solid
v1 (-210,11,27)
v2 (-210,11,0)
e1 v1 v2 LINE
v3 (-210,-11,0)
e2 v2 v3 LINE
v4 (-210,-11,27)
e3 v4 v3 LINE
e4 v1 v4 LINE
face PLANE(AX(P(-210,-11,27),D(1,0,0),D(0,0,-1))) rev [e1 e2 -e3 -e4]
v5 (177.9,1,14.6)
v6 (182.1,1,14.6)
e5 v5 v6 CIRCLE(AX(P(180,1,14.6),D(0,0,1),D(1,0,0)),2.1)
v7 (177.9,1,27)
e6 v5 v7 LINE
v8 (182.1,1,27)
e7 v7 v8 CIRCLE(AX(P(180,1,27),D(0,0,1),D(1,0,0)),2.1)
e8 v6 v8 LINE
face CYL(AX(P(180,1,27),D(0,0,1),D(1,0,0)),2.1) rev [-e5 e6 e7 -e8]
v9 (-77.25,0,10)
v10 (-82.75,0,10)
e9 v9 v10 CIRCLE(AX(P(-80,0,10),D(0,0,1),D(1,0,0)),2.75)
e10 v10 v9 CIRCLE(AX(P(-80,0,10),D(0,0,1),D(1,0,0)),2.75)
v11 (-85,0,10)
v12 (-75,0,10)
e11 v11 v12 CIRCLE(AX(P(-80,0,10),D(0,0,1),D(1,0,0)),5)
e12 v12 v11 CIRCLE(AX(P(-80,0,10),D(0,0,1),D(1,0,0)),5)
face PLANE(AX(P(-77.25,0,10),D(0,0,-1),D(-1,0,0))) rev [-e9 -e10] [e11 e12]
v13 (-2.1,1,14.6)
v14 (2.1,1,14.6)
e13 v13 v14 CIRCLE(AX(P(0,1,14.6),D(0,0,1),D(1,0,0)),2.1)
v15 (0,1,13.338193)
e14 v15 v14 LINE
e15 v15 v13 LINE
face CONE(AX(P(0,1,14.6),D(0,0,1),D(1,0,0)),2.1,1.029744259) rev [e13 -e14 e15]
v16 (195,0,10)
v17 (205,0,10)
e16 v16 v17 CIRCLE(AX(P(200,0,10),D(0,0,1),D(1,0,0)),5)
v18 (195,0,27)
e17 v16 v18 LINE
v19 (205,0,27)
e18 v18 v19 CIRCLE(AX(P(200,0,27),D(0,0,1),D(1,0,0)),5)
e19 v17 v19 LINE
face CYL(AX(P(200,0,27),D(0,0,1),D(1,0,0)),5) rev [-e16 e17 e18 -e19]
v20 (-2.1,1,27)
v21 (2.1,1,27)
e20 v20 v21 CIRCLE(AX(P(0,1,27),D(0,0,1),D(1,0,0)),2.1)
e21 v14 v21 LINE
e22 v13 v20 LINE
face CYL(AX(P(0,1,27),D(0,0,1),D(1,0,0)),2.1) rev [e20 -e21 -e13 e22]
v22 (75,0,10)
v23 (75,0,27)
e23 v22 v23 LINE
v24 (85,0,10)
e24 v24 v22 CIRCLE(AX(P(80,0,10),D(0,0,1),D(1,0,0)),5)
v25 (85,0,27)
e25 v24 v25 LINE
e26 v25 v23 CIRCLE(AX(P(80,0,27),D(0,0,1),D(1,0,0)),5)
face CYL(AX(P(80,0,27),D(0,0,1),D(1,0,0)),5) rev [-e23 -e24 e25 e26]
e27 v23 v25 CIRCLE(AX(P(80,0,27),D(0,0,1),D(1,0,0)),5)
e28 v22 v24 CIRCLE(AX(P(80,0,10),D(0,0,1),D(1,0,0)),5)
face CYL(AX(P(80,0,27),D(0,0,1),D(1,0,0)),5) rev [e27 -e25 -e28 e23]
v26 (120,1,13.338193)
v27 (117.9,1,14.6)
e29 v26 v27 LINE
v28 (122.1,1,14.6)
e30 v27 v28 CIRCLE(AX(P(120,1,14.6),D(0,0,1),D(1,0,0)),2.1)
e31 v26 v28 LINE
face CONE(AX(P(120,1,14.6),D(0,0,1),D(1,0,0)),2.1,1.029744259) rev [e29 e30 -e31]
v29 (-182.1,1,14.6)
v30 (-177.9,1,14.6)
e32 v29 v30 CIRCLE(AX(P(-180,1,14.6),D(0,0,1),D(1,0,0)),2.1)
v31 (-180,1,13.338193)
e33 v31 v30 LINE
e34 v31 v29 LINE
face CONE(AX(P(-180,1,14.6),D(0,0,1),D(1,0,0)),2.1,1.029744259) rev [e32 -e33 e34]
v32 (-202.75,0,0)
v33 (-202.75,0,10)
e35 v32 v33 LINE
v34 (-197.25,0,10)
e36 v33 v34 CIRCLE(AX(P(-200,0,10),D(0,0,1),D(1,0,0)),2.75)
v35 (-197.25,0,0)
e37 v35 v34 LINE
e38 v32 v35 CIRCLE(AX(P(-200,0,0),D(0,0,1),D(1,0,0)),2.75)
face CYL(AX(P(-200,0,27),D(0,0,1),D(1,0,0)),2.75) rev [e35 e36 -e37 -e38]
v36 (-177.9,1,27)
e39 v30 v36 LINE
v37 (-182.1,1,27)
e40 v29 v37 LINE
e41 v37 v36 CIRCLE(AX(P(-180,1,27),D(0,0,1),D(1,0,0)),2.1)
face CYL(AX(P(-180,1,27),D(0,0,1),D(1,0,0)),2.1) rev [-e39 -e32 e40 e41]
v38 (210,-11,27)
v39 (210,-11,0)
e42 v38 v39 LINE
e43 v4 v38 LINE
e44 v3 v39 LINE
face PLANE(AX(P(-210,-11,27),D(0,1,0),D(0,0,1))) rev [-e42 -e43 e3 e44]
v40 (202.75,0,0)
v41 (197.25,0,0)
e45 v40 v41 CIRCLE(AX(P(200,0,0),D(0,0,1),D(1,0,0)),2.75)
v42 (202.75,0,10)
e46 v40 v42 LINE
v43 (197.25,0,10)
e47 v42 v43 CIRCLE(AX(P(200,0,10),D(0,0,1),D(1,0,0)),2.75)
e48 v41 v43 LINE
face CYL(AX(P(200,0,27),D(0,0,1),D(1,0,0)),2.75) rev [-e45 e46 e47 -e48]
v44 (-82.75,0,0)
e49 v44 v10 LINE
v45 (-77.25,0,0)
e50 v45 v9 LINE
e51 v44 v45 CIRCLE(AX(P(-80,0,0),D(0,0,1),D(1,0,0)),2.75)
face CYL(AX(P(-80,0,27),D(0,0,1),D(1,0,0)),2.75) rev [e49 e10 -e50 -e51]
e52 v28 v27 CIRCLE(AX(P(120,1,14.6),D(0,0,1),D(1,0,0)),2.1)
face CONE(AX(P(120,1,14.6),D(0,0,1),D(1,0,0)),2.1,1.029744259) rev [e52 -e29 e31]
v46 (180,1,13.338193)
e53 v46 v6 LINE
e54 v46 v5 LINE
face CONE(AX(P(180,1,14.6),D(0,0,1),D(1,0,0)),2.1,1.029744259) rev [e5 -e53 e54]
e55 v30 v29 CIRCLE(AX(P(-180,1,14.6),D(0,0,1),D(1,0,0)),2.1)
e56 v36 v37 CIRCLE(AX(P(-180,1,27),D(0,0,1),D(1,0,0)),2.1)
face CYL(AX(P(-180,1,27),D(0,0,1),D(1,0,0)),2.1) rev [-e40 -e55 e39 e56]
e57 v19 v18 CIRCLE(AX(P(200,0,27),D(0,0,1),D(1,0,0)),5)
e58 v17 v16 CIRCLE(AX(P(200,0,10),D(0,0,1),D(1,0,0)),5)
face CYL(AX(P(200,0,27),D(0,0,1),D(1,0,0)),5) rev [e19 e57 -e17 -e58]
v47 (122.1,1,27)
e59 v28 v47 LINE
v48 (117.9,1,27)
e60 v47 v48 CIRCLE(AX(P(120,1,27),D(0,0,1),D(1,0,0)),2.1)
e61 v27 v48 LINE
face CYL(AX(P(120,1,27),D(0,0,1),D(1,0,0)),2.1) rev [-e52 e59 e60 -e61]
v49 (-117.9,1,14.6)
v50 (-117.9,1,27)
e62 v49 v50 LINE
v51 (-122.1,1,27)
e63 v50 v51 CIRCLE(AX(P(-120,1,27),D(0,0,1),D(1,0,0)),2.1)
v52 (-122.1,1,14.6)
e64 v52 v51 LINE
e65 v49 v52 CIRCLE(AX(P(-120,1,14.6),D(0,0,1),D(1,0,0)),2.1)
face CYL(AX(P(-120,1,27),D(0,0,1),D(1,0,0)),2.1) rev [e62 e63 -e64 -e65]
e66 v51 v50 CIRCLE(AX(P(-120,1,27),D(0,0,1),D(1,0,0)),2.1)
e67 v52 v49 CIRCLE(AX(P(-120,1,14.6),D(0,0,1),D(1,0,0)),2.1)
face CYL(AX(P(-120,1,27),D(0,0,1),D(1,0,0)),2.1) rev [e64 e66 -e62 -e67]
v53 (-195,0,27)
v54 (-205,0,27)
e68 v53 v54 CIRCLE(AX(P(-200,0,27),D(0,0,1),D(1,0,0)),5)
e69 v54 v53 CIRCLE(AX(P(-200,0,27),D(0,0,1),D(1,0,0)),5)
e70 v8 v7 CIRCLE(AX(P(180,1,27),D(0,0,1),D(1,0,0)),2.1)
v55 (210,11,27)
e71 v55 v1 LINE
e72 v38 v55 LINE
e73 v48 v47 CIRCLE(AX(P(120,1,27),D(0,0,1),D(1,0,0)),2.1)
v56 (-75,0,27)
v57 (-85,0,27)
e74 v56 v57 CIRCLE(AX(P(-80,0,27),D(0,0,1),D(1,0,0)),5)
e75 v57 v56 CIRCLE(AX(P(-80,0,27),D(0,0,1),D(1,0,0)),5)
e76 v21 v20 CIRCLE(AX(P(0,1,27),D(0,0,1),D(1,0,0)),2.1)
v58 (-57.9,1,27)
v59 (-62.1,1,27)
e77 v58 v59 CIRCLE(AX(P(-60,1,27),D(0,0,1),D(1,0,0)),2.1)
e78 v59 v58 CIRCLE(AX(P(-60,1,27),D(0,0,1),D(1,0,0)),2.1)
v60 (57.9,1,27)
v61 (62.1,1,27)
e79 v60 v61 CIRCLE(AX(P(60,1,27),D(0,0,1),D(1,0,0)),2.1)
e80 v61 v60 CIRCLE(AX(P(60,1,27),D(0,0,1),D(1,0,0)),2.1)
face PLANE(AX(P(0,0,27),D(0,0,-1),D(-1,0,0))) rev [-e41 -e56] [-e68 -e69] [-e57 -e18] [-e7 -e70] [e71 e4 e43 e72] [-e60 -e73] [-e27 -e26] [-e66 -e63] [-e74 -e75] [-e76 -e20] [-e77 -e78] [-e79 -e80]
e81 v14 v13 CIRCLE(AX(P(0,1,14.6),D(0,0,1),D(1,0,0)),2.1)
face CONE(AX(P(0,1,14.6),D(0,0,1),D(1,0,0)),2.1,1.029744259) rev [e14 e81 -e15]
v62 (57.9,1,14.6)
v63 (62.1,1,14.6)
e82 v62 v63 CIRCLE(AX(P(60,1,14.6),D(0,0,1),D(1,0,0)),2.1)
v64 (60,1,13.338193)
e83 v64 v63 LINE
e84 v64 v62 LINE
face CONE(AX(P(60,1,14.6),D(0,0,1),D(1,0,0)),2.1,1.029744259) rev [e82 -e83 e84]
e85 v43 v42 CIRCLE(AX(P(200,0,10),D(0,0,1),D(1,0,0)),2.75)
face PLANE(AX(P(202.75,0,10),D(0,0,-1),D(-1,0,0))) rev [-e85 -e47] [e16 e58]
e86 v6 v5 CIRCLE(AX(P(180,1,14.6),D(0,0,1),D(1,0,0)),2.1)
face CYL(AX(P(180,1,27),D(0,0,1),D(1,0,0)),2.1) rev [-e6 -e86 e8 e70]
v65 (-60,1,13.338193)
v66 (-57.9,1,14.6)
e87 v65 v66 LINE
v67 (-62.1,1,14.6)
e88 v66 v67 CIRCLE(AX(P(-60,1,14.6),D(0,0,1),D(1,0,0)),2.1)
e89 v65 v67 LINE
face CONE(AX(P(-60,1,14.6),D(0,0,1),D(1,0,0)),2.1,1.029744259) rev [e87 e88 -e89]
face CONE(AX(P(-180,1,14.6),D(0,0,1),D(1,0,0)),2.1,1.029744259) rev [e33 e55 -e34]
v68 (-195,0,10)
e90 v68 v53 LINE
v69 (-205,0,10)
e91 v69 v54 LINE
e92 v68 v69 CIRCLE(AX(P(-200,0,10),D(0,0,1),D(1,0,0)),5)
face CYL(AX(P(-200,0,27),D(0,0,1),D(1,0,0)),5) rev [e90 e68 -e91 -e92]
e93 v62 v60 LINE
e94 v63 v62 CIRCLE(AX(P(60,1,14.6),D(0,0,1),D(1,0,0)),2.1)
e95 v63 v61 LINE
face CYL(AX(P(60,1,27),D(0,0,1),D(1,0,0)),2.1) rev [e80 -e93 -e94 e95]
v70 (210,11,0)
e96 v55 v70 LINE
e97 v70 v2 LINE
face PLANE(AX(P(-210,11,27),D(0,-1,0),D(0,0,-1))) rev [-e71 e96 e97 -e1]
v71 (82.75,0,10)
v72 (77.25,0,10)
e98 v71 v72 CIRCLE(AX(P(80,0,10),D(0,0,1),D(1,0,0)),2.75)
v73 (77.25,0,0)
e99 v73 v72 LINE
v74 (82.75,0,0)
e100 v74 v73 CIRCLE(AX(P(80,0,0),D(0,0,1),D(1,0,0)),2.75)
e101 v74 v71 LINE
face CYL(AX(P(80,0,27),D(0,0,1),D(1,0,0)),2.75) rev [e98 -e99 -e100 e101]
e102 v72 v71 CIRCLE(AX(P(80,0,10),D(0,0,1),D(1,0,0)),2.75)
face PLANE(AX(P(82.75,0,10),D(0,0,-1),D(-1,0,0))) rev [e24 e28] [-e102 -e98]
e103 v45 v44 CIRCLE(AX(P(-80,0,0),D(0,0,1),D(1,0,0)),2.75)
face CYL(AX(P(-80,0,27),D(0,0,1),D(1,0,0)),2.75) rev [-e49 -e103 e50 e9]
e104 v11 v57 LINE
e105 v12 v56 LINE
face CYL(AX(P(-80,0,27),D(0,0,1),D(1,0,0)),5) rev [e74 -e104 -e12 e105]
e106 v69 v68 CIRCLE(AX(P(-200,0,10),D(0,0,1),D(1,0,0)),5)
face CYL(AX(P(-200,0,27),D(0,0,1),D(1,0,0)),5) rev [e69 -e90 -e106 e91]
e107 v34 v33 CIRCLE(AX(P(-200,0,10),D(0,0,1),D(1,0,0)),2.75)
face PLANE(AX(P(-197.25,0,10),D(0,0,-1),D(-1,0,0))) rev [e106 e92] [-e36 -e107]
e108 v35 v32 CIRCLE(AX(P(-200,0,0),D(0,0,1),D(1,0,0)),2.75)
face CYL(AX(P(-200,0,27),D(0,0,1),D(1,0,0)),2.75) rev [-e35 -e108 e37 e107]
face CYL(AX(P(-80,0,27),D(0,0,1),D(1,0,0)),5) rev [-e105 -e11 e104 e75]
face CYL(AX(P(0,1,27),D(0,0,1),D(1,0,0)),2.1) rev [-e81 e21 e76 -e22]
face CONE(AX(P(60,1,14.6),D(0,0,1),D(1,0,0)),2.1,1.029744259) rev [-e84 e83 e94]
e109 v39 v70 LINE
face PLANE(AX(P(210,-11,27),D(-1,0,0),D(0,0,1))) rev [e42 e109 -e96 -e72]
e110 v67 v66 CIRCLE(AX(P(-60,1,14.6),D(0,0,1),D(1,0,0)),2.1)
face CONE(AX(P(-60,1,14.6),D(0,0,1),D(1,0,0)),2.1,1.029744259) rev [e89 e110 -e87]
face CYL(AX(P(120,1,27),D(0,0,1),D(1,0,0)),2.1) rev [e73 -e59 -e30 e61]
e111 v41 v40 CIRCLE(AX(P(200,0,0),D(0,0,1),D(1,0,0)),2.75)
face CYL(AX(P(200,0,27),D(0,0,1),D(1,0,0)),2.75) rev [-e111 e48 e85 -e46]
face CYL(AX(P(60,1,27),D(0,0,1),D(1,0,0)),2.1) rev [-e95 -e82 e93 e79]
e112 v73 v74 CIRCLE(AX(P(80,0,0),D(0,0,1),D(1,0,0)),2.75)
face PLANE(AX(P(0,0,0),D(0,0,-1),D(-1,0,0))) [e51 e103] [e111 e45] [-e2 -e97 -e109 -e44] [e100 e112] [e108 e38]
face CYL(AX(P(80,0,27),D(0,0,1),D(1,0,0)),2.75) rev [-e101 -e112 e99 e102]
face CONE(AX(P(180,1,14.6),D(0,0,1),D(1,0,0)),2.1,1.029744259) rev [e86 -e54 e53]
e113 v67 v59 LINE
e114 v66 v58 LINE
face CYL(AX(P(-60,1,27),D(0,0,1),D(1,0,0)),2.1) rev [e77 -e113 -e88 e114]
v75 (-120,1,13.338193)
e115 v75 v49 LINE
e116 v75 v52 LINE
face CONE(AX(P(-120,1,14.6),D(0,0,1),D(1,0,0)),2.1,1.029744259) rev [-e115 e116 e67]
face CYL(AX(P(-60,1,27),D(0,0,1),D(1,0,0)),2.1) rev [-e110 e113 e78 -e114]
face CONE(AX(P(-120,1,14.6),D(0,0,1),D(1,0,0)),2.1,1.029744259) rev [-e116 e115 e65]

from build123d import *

# Parameters (mm, degrees)
SKETCH1_W                                           = 420
SKETCH1_H                                           = 22
BOSS_EXTRUDE1_DEPTH                                 = 27
M5_TAPPED_HOLE1_D                                   = 4.2
M5_TAPPED_HOLE1_DEPTH                               = 12.4
M5_TAPPED_HOLE1_TIP                                 = 1.2618073
CBORE_FOR_M5_HEX_SOCKET_HEAD_CAP_SCREW1_D           = 5.5
CBORE_FOR_M5_HEX_SOCKET_HEAD_CAP_SCREW1_CBORE_D     = 10
CBORE_FOR_M5_HEX_SOCKET_HEAD_CAP_SCREW1_CBORE_DEPTH = 17


with BuildPart() as part:
    # Sketch1 → Boss-Extrude1 (new body)
    with BuildSketch(Plane.XY):
        Rectangle(SKETCH1_W, SKETCH1_H)
    extrude(amount=BOSS_EXTRUDE1_DEPTH)

    # M5 Tapped Hole1
    with Locations(Plane.XY.offset(27)):
        with Locations((-180, 1), (-120, 1), (-60, 1), (0, 1), (60, 1), (120, 1), (180, 1)):
            Hole(M5_TAPPED_HOLE1_D / 2, depth=M5_TAPPED_HOLE1_DEPTH)
            with Locations((0, 0, -(M5_TAPPED_HOLE1_DEPTH + M5_TAPPED_HOLE1_TIP / 2))):  # 118° drill point
                Cone(0, M5_TAPPED_HOLE1_D / 2, M5_TAPPED_HOLE1_TIP, mode=Mode.SUBTRACT)

    # CBORE for M5 Hex Socket Head Cap Screw1 (through all)
    with Locations(Plane.XY.offset(27)):
        with Locations((-200, 0), (-80, 0), (80, 0), (200, 0)):
            CounterBoreHole(CBORE_FOR_M5_HEX_SOCKET_HEAD_CAP_SCREW1_D / 2, CBORE_FOR_M5_HEX_SOCKET_HEAD_CAP_SCREW1_CBORE_D / 2, CBORE_FOR_M5_HEX_SOCKET_HEAD_CAP_SCREW1_CBORE_DEPTH)


solid = part.part
